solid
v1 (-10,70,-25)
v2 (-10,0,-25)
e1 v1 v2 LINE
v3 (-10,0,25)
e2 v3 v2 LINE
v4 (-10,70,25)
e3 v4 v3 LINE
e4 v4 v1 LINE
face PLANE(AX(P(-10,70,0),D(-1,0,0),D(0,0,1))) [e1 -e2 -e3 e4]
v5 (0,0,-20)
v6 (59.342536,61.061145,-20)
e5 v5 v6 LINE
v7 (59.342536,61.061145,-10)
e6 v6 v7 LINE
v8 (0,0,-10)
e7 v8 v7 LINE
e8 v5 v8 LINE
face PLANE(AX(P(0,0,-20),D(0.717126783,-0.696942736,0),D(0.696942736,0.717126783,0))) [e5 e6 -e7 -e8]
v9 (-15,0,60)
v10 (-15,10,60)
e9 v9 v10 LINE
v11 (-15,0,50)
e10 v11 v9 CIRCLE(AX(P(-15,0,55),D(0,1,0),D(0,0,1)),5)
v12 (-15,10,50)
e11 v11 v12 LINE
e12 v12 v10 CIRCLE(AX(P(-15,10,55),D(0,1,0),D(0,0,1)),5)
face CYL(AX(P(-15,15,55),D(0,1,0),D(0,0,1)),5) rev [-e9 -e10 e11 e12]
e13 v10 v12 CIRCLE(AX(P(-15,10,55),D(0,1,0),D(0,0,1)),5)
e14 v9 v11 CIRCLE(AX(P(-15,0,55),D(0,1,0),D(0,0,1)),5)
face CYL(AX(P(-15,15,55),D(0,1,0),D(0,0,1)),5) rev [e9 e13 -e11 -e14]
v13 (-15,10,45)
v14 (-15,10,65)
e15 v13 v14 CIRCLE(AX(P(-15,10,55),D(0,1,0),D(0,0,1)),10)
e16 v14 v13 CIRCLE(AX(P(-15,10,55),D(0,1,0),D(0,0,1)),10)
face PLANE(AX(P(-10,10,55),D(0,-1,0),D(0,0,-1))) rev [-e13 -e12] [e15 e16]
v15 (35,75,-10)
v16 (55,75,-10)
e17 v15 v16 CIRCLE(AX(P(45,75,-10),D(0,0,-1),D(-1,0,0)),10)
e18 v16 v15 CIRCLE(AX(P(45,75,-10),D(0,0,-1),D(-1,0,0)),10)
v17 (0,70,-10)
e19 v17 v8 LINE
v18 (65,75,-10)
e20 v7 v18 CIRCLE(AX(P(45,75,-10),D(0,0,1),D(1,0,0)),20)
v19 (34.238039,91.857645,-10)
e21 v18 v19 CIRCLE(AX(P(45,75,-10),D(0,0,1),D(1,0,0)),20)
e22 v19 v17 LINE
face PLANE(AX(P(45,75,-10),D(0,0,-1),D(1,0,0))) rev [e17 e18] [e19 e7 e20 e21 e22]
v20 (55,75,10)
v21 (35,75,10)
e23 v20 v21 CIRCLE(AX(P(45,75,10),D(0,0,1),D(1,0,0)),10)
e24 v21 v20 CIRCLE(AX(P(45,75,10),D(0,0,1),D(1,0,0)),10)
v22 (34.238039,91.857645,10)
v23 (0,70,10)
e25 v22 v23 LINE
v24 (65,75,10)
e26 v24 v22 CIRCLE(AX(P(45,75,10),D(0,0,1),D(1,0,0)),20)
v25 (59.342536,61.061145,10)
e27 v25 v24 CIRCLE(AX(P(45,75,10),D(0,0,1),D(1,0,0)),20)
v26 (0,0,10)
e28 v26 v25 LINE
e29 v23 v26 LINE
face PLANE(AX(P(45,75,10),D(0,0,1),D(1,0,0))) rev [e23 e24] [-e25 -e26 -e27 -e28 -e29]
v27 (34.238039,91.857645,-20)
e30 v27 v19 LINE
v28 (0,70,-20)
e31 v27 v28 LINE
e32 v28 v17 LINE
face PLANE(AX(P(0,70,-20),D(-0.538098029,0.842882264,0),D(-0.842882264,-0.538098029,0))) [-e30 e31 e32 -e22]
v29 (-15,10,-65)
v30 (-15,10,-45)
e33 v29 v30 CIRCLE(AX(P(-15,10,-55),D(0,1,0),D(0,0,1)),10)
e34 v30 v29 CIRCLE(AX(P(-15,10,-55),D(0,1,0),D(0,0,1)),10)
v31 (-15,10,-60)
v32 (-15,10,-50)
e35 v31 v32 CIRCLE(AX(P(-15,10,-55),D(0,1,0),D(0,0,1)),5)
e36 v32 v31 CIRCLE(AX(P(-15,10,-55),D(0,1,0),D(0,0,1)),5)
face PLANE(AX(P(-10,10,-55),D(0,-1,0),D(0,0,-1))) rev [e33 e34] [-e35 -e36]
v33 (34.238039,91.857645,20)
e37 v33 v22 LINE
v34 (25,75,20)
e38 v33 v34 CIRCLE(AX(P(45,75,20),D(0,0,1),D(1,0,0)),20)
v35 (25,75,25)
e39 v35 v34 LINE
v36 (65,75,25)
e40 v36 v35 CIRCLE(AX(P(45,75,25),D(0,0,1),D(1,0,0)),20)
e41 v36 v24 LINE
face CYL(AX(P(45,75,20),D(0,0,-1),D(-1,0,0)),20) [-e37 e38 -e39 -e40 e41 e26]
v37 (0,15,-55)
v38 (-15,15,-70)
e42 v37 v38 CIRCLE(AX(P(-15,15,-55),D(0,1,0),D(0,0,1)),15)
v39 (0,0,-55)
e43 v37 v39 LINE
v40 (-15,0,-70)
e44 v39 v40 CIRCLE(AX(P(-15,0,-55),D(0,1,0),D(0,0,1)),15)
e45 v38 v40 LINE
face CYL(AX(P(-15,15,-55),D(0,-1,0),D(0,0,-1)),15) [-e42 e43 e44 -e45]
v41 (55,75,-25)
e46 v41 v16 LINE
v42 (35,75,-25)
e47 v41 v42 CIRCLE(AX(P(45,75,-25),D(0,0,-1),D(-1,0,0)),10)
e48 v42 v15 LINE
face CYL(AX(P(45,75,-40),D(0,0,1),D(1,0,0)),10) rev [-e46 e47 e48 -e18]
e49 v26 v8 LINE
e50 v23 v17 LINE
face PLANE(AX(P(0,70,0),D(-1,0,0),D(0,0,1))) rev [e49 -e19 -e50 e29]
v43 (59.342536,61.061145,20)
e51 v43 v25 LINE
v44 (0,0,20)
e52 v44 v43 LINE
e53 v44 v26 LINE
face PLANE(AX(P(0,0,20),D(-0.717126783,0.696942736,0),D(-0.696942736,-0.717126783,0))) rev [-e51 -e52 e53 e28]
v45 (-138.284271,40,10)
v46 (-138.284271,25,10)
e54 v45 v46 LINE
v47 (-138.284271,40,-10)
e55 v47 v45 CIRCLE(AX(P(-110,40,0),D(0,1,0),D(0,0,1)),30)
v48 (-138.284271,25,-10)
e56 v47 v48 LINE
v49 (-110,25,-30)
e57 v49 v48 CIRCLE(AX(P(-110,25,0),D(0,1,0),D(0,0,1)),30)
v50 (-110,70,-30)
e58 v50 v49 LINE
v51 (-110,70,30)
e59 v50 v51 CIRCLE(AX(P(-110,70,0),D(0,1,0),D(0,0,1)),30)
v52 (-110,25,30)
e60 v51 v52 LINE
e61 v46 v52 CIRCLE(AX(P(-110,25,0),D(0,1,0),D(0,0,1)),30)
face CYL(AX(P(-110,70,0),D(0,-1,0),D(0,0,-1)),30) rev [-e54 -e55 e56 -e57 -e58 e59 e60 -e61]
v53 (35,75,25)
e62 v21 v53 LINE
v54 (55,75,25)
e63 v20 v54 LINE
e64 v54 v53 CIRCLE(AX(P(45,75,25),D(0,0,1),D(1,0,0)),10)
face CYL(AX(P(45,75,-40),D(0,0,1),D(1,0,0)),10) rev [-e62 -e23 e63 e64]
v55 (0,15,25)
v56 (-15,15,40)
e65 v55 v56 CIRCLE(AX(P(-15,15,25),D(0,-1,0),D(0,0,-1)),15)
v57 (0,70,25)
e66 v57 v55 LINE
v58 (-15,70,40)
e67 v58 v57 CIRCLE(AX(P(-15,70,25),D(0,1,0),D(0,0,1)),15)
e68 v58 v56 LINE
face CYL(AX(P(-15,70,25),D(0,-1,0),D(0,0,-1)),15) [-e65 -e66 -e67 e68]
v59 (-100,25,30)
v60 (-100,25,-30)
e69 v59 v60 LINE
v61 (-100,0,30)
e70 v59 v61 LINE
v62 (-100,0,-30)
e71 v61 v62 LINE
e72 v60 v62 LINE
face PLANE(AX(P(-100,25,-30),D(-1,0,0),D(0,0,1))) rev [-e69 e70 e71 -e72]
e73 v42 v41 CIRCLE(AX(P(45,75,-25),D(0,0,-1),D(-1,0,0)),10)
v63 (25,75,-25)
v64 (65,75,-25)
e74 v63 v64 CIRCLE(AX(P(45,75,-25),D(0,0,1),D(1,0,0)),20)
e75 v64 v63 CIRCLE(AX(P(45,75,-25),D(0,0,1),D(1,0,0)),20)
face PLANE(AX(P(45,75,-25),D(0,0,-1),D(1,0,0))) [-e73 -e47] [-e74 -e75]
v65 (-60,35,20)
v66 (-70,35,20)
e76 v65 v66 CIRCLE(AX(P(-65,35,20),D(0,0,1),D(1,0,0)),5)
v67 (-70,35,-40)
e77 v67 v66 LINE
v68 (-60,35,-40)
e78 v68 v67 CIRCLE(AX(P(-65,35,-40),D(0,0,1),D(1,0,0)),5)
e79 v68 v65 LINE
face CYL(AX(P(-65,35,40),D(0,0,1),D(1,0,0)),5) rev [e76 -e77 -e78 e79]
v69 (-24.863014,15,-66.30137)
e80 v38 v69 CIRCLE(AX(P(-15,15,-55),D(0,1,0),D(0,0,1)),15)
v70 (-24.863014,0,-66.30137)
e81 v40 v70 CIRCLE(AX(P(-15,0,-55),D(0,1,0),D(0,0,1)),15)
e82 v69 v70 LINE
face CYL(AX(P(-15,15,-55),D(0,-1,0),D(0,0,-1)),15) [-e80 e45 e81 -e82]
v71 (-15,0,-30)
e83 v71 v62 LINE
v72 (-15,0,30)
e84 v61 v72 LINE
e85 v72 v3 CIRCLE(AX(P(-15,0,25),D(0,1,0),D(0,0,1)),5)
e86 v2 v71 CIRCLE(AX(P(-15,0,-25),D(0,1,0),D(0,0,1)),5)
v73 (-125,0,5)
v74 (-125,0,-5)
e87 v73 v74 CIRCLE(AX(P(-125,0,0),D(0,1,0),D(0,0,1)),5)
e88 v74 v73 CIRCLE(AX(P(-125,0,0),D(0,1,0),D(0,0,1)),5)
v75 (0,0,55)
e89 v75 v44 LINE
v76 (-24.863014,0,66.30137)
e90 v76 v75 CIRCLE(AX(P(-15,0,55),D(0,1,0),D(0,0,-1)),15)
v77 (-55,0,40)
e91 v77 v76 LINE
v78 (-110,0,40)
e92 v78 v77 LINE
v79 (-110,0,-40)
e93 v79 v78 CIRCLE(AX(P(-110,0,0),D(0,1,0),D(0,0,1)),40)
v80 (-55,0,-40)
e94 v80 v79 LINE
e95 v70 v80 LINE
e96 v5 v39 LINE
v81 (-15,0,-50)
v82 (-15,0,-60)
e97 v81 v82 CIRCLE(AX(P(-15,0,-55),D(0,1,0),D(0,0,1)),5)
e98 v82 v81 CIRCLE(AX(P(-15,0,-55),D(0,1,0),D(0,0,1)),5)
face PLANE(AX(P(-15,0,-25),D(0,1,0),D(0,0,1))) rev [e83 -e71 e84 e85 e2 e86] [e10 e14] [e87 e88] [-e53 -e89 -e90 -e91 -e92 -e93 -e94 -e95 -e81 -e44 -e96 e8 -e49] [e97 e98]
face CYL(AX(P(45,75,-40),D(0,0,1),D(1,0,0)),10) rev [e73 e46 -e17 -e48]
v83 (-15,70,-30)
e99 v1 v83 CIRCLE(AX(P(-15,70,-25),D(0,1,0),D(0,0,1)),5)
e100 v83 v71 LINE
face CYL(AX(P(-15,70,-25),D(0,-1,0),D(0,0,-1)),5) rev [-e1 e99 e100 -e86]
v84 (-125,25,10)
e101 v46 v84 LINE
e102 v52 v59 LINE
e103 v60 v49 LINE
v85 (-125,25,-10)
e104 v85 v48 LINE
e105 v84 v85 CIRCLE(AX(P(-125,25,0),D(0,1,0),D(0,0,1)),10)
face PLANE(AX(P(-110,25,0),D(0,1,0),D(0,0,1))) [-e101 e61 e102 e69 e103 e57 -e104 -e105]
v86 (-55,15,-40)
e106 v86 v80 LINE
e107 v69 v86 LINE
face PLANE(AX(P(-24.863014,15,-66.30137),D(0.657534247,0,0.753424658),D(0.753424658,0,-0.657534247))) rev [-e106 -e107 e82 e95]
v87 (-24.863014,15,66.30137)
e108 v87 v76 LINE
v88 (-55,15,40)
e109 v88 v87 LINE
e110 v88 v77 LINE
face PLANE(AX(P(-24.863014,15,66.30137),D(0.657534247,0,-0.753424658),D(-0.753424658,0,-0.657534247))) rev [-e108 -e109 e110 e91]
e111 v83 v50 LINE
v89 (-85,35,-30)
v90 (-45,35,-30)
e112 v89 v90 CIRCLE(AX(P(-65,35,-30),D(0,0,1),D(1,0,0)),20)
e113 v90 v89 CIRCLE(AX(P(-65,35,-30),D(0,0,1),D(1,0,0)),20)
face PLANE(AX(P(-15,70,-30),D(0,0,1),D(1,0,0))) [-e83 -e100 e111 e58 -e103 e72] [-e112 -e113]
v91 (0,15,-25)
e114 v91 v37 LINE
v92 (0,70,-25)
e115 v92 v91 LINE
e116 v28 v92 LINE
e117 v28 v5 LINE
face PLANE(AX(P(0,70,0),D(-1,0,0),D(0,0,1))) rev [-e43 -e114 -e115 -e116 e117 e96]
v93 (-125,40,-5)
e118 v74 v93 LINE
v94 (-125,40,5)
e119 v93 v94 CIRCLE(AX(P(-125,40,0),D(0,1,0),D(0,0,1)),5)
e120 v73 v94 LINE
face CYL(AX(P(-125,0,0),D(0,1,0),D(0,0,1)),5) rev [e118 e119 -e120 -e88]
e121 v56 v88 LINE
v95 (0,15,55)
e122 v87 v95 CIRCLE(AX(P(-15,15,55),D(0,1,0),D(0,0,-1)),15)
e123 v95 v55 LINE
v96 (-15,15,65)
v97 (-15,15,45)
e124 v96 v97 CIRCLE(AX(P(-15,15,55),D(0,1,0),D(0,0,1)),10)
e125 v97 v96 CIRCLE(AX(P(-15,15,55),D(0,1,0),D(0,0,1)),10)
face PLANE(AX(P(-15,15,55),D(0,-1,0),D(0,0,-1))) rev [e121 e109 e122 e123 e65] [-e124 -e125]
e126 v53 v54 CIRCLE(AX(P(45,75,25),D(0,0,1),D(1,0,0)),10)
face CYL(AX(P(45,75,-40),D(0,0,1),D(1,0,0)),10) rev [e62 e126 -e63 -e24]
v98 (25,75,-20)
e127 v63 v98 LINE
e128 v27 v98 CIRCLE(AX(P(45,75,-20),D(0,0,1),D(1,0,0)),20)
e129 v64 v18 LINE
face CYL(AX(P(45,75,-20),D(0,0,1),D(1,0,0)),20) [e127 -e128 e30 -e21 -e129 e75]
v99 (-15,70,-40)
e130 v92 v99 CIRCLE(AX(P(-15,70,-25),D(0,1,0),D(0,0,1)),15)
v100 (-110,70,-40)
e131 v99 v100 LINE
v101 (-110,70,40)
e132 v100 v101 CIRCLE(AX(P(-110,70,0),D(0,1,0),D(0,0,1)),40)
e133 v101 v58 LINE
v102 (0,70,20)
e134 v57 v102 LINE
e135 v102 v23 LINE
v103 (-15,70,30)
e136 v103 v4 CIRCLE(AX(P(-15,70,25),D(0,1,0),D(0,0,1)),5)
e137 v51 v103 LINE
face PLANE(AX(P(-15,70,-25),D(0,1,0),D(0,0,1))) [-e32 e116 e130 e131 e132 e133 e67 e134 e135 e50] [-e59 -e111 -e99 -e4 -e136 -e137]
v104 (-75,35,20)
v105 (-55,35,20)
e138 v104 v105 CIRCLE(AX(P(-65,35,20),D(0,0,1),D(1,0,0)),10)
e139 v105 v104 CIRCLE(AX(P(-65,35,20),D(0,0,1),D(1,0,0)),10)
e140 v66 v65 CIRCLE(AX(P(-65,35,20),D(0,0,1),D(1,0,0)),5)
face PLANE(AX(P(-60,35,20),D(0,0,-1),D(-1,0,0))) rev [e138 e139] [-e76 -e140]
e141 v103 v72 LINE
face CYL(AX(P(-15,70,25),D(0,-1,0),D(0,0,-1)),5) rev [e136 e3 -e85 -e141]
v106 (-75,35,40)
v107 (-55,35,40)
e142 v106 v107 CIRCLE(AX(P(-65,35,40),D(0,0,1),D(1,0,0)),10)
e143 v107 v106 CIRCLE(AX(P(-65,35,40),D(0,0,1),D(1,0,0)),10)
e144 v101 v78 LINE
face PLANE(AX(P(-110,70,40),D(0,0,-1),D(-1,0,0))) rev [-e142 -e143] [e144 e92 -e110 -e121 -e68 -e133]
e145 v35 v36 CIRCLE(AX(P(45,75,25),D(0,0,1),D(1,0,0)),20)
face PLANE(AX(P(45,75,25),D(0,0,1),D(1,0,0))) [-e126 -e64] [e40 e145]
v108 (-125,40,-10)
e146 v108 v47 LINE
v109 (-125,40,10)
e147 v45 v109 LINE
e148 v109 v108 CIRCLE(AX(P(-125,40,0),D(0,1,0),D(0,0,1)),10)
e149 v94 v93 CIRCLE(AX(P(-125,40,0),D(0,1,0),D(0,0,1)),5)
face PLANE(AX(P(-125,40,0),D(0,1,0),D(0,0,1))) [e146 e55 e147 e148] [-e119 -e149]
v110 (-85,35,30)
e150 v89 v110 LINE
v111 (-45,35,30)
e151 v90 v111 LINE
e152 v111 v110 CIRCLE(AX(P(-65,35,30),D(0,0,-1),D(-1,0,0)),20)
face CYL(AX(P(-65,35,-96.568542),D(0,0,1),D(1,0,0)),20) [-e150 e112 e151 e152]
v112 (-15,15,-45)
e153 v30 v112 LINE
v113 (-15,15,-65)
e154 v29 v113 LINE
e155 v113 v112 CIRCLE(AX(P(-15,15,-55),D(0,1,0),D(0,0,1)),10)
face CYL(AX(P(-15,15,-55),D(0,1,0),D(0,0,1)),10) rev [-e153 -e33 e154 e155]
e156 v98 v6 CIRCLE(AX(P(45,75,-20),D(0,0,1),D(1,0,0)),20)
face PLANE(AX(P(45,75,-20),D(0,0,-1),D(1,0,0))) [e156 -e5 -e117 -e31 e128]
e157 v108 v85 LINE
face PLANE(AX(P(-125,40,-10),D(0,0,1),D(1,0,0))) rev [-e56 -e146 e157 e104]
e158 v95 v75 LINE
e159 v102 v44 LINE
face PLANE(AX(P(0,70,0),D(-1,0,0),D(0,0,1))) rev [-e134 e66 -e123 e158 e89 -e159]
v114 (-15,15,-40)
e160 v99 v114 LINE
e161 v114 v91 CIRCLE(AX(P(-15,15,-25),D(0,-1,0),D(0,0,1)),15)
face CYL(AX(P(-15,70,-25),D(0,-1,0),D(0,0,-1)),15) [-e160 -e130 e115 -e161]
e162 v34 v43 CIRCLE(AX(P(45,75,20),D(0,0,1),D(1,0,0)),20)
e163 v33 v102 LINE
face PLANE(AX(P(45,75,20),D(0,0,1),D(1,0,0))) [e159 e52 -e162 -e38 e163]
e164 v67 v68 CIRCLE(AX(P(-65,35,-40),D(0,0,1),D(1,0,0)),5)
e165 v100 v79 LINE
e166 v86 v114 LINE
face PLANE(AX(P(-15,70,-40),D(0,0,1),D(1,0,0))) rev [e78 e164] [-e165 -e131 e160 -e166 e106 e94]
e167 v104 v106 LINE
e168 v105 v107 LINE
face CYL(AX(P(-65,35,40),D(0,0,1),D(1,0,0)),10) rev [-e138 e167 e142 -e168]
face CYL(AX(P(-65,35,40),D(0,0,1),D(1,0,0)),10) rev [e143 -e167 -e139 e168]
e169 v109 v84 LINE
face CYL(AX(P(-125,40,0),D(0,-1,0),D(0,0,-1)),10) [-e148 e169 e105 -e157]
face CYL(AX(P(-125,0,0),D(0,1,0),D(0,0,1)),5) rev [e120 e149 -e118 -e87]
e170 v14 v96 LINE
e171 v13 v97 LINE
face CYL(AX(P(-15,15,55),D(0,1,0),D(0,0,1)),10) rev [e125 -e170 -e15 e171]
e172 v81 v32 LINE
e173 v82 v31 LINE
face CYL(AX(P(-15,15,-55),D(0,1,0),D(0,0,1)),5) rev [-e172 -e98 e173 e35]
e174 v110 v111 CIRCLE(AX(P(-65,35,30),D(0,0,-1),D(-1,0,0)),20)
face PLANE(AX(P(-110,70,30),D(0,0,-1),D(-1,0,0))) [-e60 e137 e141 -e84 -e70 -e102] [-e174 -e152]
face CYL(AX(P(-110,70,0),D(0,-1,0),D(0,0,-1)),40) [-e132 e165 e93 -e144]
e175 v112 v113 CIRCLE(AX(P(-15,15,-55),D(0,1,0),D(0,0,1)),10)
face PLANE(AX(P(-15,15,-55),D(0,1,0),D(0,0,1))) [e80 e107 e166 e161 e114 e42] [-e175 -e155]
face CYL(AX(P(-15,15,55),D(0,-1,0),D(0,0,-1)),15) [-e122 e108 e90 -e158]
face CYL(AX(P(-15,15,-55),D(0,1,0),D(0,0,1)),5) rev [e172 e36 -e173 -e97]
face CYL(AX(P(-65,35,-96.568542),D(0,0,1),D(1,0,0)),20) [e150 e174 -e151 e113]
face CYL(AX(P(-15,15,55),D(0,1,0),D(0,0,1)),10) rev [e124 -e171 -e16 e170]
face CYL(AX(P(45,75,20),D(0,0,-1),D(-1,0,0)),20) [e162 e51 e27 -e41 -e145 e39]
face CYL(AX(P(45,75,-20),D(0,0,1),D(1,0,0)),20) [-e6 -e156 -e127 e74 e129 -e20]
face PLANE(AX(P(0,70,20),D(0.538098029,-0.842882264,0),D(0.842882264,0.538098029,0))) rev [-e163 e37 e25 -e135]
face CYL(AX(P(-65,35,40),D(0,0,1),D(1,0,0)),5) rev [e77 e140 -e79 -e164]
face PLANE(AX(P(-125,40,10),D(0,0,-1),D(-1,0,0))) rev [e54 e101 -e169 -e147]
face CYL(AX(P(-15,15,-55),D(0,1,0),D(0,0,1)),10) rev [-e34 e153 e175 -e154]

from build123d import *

# Parameters (mm, degrees)
POCKET_HOUSING_DEPTH                   = 70
SWIVEL_BOSS_DEPTH                      = 25
SWIVEL_BLOCK_DEPTH                     = 15
SWIVEL_PIN_HOLE_SKETCH_R               = 5
SWIVEL_PIN_HOLE_10_DEPTH               = 161.312195419
CLEVIS_START                           = 10
CLEVIS_LUG_DEPTH                       = 10
LUG_HUB_SKETCH_R                       = 20
LUG_HUB_DEPTH                          = 5
LUG_BORE_20_DEPTH                      = 190.076704012
LUG_BORE_20_DEPTH_BACK                 = 190.076704012
LUG_BORE_SKETCH_R                      = 10
PIVOT_BOSS_SKETCH_R                    = 20
PIVOT_BOSS_40_DEPTH                    = 80
PIVOT_COUNTERBORED_HOLE_10_D           = 10
PIVOT_COUNTERBORED_HOLE_10_CBORE_D     = 20
PIVOT_COUNTERBORED_HOLE_10_CBORE_DEPTH = 20
MOUNTING_TAB_DEPTH                     = 15
TAB_COUNTERBORED_HOLE_10_D             = 10
TAB_COUNTERBORED_HOLE_10_CBORE_D       = 20
TAB_COUNTERBORED_HOLE_10_CBORE_DEPTH   = 5


with BuildPart() as part:
    # Pocket Housing Sketch → Pocket Housing (new body)
    with BuildSketch(Plane(origin=(0, 0, 0), x_dir=(1, 0, 0), z_dir=(0, 1, 0))):
        with BuildLine():
            Line((0, 0), (0, 25))
            ThreePointArc((0, 25), (-4.393398282, 35.606601718), (-15, 40))
            Line((-15, 40), (-110, 40))
            ThreePointArc((-110, 40), (-150, 0), (-110, -40))
            Line((-110, -40), (-15, -40))
            ThreePointArc((-15, -40), (-4.393398282, -35.606601718), (0, -25))
            Line((0, -25), (0, 0))
        make_face()
        with BuildLine():
            Line((-15, 30), (-110, 30))
            ThreePointArc((-110, 30), (-140, 0), (-110, -30))
            Line((-110, -30), (-15, -30))
            ThreePointArc((-15, -30), (-11.464466094, -28.535533906), (-10, -25))
            Line((-10, -25), (-10, 0))
            Line((-10, 0), (-10, 25))
            ThreePointArc((-10, 25), (-11.464466094, 28.535533906), (-15, 30))
        make_face(mode=Mode.SUBTRACT)
    extrude(amount=POCKET_HOUSING_DEPTH)

    # Swivel Boss Sketch → Swivel Boss (add)
    with BuildSketch(Plane(origin=(0, 0, 0), x_dir=(1, 0, 0), z_dir=(0, 1, 0))):
        with BuildLine():
            Line((-100, 30), (-100, -30))
            Line((-100, -30), (-110, -30))
            ThreePointArc((-110, -30), (-140, 0), (-110, 30))
            Line((-110, 30), (-100, 30))
        make_face()
    extrude(amount=SWIVEL_BOSS_DEPTH)

    # Swivel Block Sketch → Swivel Block (add)
    with BuildSketch(Plane(origin=(0, 25, 0), x_dir=(1, 0, 0), z_dir=(0, 1, 0))):
        with BuildLine():
            Line((-125, -10), (-138.284271247, -10))
            ThreePointArc((-138.284271247, -10), (-140, 0), (-138.284271247, 10))
            Line((-138.284271247, 10), (-125, 10))
            ThreePointArc((-125, 10), (-115, 0), (-125, -10))
        make_face()
    extrude(amount=SWIVEL_BLOCK_DEPTH)

    # Swivel Pin Hole Sketch → Swivel Pin Hole Ø10 (cut, through all)
    with BuildSketch(Plane(origin=(0, 40, 0), x_dir=(1, 0, 0), z_dir=(0, 1, 0))):
        with Locations(Location((-125, 0, 0), (0, 0, 270))):
            Circle(SWIVEL_PIN_HOLE_SKETCH_R)
    extrude(amount=-SWIVEL_PIN_HOLE_10_DEPTH, mode=Mode.SUBTRACT)

    # Clevis Lug Sketch → Clevis Lug (add)
    with BuildSketch(Plane.XY.offset(CLEVIS_START)):
        with BuildLine():
            Line((0, 70), (34.238039414, 91.857645278))
            ThreePointArc((34.238039414, 91.857645278), (60.501975118, 87.636802105), (59.342535653, 61.061145275))
            Line((59.342535653, 61.061145275), (0, 0))
            Line((0, 0), (0, 70))
        make_face()
    clevis_lug = extrude(amount=CLEVIS_LUG_DEPTH)

    # Lug Hub Sketch → Lug Hub (add)
    with BuildSketch(Plane.XY.offset(20)):
        with Locations(Location((45, 75, 0), (0, 0, 122.554257086))):
            Circle(LUG_HUB_SKETCH_R)
    lug_hub = extrude(amount=LUG_HUB_DEPTH)

    # Clevis Lug Mirror: Clevis Lug, Lug Hub across plane
    add(clevis_lug.mirror(Plane.XY))
    add(lug_hub.mirror(Plane.XY))

    # Lug Bore Sketch → Lug Bore Ø20 (cut, two sides: drawn at the far end of the back side and taken through both)
    with BuildSketch(Plane.XY.offset(25).offset(-LUG_BORE_20_DEPTH_BACK)):
        with Locations(Location((45, 75, 0), (0, 0, 180))):
            Circle(LUG_BORE_SKETCH_R)
    extrude(amount=LUG_BORE_20_DEPTH + LUG_BORE_20_DEPTH_BACK, mode=Mode.SUBTRACT)

    # Pivot Boss Sketch → Pivot Boss Ø40 (add)
    with BuildSketch(Plane.XY.offset(40)):
        with Locations((-65, 35)):
            Circle(PIVOT_BOSS_SKETCH_R)
    extrude(amount=-PIVOT_BOSS_40_DEPTH)

    # Pivot Counterbored Hole Ø10 (through all)
    with Locations(Plane(origin=(-65, 35, 40), x_dir=(1, 0, 0), z_dir=(0, 0, 1))):
        with Locations((0, 0)):
            CounterBoreHole(PIVOT_COUNTERBORED_HOLE_10_D / 2, PIVOT_COUNTERBORED_HOLE_10_CBORE_D / 2, PIVOT_COUNTERBORED_HOLE_10_CBORE_DEPTH)

    # Mounting Tab Sketch → Mounting Tab (add)
    with BuildSketch(Plane(origin=(0, 0, 0), x_dir=(1, 0, 0), z_dir=(0, 1, 0))):
        with BuildLine():
            Line((0, 25), (0, 55))
            ThreePointArc((0, 55), (-8.792955835, 68.655497162), (-24.863013699, 66.301369863))
            Line((-24.863013699, 66.301369863), (-55, 40))
            Line((-55, 40), (-15, 40))
            ThreePointArc((-15, 40), (-4.393398282, 35.606601718), (0, 25))
        make_face()
        with BuildLine():
            Line((0, -25), (0, -55))
            ThreePointArc((0, -55), (-8.792955835, -68.655497162), (-24.863013699, -66.301369863))
            Line((-24.863013699, -66.301369863), (-55, -40))
            Line((-55, -40), (-15, -40))
            ThreePointArc((-15, -40), (-4.393398282, -35.606601718), (0, -25))
        make_face()
    extrude(amount=MOUNTING_TAB_DEPTH)

    # Tab Counterbored Hole Ø10 (through all)
    with Locations(Plane(origin=(-15, 15, 55), x_dir=(0, 0, 1), z_dir=(0, 1, 0))):
        with Locations((0, 0), (-110, 0)):
            CounterBoreHole(TAB_COUNTERBORED_HOLE_10_D / 2, TAB_COUNTERBORED_HOLE_10_CBORE_D / 2, TAB_COUNTERBORED_HOLE_10_CBORE_DEPTH)


solid = part.part
